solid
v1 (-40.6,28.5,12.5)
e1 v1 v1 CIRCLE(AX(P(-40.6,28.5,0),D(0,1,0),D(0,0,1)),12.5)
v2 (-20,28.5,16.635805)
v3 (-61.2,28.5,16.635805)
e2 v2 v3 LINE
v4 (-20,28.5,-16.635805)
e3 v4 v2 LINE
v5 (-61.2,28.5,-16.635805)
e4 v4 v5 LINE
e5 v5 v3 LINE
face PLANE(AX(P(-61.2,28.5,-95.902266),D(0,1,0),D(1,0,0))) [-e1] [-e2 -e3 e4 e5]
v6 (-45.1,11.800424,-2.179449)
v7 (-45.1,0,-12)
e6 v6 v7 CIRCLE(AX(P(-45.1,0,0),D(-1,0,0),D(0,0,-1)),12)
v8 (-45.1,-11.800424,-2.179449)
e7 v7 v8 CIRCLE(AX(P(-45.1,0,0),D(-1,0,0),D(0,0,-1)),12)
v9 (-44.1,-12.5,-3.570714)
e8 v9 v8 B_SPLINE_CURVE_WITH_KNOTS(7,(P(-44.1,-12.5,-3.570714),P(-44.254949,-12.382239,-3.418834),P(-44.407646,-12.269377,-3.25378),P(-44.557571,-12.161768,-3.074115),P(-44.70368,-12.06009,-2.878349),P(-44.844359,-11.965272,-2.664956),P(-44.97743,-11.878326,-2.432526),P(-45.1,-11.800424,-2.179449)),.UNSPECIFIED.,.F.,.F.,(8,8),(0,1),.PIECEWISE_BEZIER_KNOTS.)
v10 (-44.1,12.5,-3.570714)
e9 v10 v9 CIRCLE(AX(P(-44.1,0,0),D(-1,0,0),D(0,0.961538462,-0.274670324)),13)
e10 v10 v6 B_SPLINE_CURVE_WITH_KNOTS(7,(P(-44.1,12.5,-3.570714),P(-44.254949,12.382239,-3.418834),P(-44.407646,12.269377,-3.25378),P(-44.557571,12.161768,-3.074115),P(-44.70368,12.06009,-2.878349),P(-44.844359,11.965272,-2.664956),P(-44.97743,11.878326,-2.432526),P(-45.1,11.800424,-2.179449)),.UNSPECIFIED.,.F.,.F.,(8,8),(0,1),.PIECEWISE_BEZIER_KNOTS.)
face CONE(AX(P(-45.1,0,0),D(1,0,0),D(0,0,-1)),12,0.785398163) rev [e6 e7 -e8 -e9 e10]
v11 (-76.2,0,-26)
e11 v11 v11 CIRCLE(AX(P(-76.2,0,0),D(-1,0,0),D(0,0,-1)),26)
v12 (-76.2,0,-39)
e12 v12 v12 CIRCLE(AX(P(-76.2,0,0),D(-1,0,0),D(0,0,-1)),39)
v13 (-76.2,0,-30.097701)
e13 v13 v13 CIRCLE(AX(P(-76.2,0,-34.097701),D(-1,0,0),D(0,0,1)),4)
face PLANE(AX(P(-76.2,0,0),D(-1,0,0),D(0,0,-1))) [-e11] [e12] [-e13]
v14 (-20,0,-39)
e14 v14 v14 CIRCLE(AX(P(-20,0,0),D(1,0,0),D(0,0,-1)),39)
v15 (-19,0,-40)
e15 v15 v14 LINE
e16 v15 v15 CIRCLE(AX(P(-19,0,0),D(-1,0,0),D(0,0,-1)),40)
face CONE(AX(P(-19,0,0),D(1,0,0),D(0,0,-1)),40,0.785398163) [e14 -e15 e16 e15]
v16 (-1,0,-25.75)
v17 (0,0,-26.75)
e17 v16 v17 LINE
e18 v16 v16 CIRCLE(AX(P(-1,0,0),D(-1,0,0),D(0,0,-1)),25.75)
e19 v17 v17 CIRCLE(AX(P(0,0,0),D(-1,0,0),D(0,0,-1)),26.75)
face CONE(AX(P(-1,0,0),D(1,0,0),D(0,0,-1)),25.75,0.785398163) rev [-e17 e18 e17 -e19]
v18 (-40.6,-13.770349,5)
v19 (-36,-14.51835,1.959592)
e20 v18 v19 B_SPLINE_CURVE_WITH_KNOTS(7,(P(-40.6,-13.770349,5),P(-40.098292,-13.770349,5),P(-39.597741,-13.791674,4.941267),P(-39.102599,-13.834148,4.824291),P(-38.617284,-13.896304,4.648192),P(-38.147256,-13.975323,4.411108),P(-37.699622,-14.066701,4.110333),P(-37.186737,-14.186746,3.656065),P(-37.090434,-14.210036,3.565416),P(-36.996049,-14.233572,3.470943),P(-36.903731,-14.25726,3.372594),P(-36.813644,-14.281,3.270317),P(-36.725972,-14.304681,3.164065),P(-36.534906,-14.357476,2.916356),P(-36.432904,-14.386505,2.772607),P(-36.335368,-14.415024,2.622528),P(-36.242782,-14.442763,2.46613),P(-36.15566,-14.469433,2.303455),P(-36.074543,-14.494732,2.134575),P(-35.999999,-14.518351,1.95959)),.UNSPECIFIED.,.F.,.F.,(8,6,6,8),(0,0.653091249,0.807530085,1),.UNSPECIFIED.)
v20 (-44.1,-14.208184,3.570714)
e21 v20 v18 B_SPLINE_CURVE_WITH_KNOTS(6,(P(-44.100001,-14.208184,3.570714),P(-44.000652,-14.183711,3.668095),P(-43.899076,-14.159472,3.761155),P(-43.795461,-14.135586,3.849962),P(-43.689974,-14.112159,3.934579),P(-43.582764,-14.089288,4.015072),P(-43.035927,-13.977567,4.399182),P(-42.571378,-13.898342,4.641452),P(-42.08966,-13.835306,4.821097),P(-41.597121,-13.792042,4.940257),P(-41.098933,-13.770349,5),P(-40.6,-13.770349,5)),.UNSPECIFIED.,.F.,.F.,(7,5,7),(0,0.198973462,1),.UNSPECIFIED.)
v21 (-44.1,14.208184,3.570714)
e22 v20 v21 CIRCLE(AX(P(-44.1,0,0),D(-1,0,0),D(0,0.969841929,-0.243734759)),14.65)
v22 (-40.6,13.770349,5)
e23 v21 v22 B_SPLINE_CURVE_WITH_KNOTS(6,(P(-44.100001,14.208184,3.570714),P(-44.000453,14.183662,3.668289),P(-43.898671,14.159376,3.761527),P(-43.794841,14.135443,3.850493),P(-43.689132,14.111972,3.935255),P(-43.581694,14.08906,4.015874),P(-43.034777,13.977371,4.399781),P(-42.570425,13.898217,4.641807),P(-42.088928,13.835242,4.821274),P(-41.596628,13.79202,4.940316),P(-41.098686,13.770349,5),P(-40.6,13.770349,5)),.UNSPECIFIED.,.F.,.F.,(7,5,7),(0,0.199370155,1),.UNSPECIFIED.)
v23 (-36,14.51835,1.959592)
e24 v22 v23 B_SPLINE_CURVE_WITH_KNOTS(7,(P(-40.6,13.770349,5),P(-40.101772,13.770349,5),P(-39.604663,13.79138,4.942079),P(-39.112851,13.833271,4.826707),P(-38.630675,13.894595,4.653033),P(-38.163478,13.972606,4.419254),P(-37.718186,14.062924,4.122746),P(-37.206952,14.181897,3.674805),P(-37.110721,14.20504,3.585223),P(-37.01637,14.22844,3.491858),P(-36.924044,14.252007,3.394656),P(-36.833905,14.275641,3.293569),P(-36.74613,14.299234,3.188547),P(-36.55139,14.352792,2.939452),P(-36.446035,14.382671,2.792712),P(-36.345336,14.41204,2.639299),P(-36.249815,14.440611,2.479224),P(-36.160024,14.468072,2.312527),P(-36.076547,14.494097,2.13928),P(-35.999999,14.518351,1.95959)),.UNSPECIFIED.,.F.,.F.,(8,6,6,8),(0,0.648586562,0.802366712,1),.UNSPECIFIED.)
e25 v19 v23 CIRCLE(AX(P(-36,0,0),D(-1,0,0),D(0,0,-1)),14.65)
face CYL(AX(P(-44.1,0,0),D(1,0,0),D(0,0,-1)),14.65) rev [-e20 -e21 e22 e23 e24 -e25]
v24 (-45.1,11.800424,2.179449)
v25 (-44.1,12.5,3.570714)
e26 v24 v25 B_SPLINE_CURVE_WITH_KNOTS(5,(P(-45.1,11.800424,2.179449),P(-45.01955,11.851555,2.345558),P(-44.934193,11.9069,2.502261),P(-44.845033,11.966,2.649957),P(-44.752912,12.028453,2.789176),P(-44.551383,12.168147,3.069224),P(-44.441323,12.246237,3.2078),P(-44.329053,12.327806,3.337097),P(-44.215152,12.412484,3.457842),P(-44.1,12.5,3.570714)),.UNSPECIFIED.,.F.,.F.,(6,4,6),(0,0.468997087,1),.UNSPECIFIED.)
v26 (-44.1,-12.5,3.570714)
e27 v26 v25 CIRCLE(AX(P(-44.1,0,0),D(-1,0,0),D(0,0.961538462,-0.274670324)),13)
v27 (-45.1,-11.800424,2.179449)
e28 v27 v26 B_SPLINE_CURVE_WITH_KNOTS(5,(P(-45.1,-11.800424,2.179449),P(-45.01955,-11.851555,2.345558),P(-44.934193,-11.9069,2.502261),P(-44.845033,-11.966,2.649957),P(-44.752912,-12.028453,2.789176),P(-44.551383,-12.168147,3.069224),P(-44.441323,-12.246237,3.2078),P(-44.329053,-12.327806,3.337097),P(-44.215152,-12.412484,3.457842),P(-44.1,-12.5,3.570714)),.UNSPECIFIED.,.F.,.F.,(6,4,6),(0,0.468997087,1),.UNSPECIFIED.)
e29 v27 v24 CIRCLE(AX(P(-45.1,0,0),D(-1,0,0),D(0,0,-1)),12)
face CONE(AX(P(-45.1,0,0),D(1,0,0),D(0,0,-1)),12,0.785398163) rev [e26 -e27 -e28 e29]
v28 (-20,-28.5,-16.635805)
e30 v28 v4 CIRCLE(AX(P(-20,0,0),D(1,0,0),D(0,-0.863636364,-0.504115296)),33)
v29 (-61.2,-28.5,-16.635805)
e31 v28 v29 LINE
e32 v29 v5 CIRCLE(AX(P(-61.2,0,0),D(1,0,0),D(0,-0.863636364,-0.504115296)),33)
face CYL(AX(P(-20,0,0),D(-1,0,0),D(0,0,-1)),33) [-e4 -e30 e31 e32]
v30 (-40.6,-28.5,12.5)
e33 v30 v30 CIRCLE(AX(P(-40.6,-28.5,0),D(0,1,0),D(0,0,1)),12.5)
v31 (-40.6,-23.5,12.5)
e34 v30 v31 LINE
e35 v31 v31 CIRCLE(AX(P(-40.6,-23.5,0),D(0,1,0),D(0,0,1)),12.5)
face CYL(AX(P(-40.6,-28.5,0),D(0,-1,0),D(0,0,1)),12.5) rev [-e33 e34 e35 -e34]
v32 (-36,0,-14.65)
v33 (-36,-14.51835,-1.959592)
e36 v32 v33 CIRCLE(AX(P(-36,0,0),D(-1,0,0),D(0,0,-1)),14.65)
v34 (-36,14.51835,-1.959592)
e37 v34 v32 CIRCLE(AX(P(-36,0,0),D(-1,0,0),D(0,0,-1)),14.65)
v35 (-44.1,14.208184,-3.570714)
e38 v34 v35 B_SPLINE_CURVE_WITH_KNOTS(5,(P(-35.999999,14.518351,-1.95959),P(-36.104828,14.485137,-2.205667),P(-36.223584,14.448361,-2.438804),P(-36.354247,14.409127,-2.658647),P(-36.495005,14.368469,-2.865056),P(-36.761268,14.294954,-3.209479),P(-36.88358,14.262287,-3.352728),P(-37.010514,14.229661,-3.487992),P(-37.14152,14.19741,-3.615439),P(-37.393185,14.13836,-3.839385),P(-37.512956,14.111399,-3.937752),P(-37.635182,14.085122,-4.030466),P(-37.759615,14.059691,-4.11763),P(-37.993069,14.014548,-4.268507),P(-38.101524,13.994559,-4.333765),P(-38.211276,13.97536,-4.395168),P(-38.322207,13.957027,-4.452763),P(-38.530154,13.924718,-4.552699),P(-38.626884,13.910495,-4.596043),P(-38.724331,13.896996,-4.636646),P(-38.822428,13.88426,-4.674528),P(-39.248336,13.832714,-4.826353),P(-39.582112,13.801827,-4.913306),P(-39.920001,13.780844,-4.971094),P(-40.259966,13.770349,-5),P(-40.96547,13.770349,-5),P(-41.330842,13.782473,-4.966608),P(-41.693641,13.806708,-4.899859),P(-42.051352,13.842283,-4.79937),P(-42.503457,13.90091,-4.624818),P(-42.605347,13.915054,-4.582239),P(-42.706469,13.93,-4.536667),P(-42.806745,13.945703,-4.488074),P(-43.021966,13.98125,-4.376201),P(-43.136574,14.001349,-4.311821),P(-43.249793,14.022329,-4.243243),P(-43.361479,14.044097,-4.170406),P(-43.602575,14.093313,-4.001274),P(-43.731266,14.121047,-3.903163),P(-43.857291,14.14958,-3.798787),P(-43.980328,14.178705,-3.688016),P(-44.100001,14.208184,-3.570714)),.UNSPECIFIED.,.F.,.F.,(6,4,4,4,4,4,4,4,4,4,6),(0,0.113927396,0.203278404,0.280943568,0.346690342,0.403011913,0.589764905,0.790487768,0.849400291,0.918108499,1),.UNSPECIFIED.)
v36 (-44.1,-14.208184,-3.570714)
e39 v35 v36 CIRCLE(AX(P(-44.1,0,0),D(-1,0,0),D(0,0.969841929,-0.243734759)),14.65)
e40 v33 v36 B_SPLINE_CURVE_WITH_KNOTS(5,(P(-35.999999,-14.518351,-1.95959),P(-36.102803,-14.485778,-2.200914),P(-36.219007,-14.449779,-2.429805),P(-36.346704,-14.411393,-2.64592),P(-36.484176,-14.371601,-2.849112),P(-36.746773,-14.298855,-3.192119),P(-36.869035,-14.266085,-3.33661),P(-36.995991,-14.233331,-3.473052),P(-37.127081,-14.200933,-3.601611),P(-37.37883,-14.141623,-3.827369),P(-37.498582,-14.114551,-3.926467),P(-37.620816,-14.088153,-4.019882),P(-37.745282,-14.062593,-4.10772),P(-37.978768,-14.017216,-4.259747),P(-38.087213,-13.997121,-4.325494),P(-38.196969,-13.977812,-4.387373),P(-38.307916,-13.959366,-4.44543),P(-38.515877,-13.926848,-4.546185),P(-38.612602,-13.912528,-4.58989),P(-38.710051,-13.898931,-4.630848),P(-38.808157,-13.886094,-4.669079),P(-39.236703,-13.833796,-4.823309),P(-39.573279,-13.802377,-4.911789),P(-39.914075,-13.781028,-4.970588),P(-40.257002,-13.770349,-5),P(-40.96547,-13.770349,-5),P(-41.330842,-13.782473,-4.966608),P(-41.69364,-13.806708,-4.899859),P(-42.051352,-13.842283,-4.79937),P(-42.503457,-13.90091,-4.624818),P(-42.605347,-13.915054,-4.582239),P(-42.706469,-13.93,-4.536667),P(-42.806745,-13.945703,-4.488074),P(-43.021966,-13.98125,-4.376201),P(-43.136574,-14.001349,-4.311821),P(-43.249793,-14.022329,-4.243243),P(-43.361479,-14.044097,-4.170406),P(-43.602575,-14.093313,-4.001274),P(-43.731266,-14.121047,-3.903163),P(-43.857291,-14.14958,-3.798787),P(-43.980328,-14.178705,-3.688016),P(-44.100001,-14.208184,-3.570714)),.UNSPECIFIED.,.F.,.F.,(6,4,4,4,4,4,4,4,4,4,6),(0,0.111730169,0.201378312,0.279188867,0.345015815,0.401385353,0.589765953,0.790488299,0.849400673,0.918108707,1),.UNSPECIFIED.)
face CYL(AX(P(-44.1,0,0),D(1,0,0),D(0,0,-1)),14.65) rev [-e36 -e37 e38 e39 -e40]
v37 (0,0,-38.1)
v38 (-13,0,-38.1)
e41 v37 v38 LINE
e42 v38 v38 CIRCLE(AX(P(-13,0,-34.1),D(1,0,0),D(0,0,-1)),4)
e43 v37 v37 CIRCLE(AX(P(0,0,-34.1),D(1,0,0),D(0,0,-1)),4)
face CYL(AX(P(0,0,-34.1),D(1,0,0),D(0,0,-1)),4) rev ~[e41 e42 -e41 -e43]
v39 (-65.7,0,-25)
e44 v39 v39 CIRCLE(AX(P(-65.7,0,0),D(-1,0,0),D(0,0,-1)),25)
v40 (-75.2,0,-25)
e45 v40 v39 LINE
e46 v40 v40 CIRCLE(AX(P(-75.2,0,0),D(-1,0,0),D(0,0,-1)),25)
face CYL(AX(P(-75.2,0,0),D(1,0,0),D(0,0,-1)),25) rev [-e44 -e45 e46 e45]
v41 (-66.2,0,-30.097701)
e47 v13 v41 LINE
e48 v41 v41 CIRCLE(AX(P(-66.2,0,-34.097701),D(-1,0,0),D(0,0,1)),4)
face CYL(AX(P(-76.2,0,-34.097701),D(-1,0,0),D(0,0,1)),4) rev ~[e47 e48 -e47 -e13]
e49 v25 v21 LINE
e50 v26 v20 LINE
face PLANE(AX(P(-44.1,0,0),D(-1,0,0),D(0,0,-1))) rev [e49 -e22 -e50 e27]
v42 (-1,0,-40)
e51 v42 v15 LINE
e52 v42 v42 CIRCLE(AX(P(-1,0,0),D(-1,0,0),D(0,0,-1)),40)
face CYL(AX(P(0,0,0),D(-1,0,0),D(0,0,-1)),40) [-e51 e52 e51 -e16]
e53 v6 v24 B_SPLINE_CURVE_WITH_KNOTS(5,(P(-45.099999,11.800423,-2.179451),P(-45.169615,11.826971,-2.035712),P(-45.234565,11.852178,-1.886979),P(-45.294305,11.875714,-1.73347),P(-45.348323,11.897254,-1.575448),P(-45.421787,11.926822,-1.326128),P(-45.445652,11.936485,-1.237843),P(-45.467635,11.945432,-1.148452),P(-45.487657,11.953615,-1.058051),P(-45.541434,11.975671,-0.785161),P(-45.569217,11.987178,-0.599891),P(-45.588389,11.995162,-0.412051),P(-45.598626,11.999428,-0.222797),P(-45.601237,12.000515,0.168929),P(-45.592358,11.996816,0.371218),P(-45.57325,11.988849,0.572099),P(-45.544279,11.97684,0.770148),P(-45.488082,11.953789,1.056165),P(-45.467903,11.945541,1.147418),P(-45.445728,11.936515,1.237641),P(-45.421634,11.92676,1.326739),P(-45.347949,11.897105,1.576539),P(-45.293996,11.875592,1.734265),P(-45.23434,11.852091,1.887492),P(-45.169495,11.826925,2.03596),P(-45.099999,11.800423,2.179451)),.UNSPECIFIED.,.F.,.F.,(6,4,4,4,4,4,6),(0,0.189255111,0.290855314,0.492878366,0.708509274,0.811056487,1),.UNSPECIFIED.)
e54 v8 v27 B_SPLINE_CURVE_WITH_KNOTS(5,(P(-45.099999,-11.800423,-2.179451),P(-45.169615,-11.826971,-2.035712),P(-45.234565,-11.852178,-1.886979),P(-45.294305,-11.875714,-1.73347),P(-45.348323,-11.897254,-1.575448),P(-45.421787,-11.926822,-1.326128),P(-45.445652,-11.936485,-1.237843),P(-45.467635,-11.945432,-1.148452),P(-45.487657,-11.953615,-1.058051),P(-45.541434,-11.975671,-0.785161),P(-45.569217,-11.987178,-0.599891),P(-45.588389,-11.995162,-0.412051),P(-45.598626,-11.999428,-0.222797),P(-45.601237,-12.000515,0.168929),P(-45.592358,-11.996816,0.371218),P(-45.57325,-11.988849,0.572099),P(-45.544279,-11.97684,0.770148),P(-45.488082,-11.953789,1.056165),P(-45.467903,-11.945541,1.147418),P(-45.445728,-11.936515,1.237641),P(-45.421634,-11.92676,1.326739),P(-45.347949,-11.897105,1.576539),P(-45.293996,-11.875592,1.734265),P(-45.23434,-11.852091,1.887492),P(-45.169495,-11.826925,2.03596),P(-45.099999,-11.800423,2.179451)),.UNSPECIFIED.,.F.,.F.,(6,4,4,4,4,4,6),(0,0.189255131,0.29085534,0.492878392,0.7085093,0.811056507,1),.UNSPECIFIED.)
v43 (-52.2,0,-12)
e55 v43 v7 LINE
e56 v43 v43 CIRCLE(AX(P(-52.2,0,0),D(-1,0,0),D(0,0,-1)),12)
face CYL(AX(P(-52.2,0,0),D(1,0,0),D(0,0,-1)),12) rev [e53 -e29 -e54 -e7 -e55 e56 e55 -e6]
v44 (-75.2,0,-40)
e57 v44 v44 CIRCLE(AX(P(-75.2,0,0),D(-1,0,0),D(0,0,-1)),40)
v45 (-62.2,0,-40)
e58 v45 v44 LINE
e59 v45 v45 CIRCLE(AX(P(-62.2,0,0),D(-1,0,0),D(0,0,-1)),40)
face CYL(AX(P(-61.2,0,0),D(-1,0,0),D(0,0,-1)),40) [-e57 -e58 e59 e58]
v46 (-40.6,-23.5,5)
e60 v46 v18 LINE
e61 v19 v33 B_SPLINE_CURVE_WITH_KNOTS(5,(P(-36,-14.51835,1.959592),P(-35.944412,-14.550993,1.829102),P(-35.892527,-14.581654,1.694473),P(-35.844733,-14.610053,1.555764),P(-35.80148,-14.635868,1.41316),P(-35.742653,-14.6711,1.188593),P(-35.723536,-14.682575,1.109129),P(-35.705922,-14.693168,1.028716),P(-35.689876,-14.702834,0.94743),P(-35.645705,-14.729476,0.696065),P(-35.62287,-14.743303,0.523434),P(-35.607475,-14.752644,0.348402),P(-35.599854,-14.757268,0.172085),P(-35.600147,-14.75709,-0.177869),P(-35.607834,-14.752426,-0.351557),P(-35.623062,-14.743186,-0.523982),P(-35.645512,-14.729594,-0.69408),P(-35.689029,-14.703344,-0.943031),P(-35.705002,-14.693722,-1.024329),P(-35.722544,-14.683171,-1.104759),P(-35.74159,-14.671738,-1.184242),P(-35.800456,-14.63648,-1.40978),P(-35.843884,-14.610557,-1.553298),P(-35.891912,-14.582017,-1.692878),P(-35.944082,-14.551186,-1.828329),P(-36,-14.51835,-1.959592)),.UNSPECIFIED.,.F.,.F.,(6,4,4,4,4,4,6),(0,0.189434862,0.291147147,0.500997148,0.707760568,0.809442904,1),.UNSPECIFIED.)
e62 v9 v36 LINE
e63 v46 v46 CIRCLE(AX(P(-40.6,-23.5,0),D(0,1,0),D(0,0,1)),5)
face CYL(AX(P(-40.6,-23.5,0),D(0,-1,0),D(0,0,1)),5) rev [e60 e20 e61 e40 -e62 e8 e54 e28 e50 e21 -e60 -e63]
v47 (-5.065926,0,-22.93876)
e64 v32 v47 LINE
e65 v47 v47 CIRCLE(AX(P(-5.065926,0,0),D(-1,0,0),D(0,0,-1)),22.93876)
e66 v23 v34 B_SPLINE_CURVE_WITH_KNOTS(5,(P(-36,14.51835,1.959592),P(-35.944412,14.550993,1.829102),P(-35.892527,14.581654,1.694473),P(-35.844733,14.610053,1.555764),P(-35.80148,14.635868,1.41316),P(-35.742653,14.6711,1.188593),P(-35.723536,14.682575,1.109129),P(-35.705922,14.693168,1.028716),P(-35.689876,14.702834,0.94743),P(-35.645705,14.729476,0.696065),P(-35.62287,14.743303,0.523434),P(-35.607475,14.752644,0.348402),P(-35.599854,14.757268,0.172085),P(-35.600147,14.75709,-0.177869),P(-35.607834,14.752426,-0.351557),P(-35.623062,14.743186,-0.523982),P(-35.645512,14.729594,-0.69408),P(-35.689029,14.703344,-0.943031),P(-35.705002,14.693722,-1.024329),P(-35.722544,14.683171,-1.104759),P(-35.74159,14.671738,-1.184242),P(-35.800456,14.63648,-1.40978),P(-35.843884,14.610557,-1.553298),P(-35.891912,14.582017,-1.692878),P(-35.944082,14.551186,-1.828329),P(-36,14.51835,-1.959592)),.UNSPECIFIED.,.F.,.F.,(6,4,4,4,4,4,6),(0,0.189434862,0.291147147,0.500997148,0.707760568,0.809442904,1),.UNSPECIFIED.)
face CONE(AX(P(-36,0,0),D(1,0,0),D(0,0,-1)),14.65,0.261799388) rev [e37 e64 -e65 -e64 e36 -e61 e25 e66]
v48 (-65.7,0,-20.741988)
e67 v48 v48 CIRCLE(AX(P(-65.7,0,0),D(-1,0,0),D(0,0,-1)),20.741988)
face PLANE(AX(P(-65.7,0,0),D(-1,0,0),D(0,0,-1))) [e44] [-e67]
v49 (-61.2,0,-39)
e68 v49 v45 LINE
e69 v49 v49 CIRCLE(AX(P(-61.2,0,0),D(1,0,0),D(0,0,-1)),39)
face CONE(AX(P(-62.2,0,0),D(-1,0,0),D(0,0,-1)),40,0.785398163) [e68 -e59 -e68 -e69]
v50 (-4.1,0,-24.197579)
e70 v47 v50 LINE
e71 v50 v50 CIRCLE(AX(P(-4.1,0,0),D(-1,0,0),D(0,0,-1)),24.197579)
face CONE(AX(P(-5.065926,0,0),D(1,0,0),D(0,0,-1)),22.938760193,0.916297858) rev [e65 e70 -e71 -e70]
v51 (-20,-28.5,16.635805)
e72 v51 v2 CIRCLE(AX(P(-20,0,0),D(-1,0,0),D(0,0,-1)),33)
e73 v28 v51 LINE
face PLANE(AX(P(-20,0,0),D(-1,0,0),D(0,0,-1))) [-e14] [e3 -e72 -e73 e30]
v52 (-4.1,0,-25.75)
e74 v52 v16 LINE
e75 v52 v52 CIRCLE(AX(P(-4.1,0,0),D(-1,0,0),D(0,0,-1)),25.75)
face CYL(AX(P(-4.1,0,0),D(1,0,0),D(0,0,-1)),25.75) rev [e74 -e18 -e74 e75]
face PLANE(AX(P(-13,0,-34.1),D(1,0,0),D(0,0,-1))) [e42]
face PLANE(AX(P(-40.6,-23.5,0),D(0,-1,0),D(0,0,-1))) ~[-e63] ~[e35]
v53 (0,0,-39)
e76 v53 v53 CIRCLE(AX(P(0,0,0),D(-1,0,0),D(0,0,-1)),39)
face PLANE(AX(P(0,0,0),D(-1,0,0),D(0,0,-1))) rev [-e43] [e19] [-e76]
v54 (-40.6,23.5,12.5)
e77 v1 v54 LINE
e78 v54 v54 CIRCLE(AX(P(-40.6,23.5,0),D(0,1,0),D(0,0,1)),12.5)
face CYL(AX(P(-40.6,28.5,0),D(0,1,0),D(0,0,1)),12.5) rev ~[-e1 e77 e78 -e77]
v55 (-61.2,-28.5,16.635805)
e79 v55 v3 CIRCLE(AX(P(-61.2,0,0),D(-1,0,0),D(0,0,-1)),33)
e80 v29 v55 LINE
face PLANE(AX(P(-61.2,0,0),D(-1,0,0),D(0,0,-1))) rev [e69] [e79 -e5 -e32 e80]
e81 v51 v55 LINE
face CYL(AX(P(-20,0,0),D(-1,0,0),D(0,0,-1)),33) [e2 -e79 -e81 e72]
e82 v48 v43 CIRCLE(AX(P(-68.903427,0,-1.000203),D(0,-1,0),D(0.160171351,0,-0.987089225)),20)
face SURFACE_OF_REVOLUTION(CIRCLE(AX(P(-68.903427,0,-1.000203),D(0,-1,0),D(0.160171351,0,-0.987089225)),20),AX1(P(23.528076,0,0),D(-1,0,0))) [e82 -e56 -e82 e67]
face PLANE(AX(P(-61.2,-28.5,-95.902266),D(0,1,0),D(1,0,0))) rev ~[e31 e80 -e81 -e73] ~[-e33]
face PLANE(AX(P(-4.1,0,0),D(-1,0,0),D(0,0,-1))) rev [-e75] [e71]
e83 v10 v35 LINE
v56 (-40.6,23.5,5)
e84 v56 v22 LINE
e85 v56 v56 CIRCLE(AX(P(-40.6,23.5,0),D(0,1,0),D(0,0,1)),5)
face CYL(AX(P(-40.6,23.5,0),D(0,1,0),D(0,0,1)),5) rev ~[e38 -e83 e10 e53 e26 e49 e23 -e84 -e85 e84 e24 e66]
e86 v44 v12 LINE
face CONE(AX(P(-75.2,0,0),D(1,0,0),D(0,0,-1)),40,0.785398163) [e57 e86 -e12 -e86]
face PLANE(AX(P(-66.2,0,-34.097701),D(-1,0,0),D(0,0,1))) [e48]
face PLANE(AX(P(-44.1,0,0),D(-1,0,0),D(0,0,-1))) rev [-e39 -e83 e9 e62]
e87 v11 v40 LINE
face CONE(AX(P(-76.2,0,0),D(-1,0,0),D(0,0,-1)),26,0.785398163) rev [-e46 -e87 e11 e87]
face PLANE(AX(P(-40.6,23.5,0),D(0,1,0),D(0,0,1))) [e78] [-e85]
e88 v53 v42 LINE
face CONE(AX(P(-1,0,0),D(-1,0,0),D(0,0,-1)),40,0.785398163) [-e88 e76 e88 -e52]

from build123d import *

# Parameters (mm, degrees)
CHAMFER1_SIZE           = 1
CUT_EXTRUDE1_DEPTH      = 95.902265516
CUT_EXTRUDE1_DEPTH_BACK = 95.902265516
SKETCH2_W               = 41.2
SKETCH2_H               = 27.770788335
SKETCH2_H_2             = 30.82392473
SKETCH3_R               = 12.5
CUT_EXTRUDE2_DEPTH      = 5
SKETCH4_R               = 5
CUT_EXTRUDE3_DEPTH      = 19
SKETCH5_R               = 4
CUT_EXTRUDE4_DEPTH      = 10
SKETCH6_R               = 4
CUT_EXTRUDE5_DEPTH      = 13


with BuildPart() as part:
    # Sketch1 → Revolve1 (revolve)
    with BuildSketch(Plane.XY, mode=Mode.PRIVATE) as revolve1_sk:
        with BuildLine():
            Line((0, 26.75), (0, 40))
            Line((0, 40), (-20, 40))
            Line((-20, 40), (-20, 33))
            Line((-20, 33), (-61.2, 33))
            Line((-61.2, 33), (-61.2, 40))
            Line((-61.2, 40), (-76.2, 40))
            Line((-76.2, 40), (-76.2, 26))
            Line((-76.2, 26), (-75.2, 25))
            Line((-75.2, 25), (-65.7, 25))
            Line((-65.7, 25), (-65.7, 20.741987874))
            ThreePointArc((-65.7, 20.741987874), (-58.03253481, 17.787808996), (-52.2, 12))
            Line((-52.2, 12), (-45.1, 12))
            Line((-45.1, 12), (-44.1, 13))
            Line((-44.1, 13), (-44.1, 14.65))
            Line((-44.1, 14.65), (-36, 14.65))
            Line((-36, 14.65), (-5.065925826, 22.938760193))
            Line((-5.065925826, 22.938760193), (-4.1, 24.197579239))
            Line((-4.1, 24.197579239), (-4.1, 25.75))
            Line((-4.1, 25.75), (-1, 25.75))
            Line((-1, 25.75), (0, 26.75))
        make_face()
    revolve(revolve1_sk.sketch.rotate(Axis((23.528076115, 0, 0), (-1, 0, 0)), 90), axis=Axis((23.528076115, 0, 0), (-1, 0, 0)))

    # Chamfer1
    chamfer1_edges = [part.edges().sort_by_distance(p)[0] for p in [
        (0, 0, 40),
        (-20, 0, 40),
        (-61.2, 0, 40),
        (-76.2, 0, 40),
    ]]
    chamfer(chamfer1_edges, length=CHAMFER1_SIZE)

    # Sketch2 → Cut-Extrude1 (cut, two sides: drawn at the far end of the back side and taken through both)
    with BuildSketch(Plane.XY.offset(-CUT_EXTRUDE1_DEPTH_BACK)):
        with Locations((-40.6, 42.385394168)):
            Rectangle(SKETCH2_W, SKETCH2_H)
        with Locations((-40.6, -43.911962365)):
            Rectangle(SKETCH2_W, SKETCH2_H_2)
    extrude(amount=CUT_EXTRUDE1_DEPTH + CUT_EXTRUDE1_DEPTH_BACK, mode=Mode.SUBTRACT)

    # Sketch3 → Cut-Extrude2 (cut)
    with BuildSketch(Plane(origin=(0, 28.5, 0), x_dir=(1, 0, 0), z_dir=(0, 1, 0))):
        with Locations(Location((-40.6, 0, 0), (0, 0, 270))):
            Circle(SKETCH3_R)
    cut_extrude2 = extrude(amount=-CUT_EXTRUDE2_DEPTH, mode=Mode.SUBTRACT)

    # Sketch4 → Cut-Extrude3 (cut)
    with BuildSketch(Plane(origin=(0, 23.5, 0), x_dir=(1, 0, 0), z_dir=(0, 1, 0))):
        with Locations(Location((-40.6, 0, 0), (0, 0, 270))):
            Circle(SKETCH4_R)
    cut_extrude3 = extrude(amount=-CUT_EXTRUDE3_DEPTH, mode=Mode.SUBTRACT)

    # Mirror1: Cut-Extrude2, Cut-Extrude3 across plane
    add(cut_extrude2.mirror(Plane.ZX), mode=Mode.SUBTRACT)
    add(cut_extrude3.mirror(Plane.ZX), mode=Mode.SUBTRACT)

    # Sketch5 → Cut-Extrude4 (cut)
    with BuildSketch(Plane.ZY.offset(76.2)):
        with Locations((-34.097701423, 0)):
            Circle(SKETCH5_R)
    extrude(amount=-CUT_EXTRUDE4_DEPTH, mode=Mode.SUBTRACT)

    # Sketch6 → Cut-Extrude5 (cut)
    with BuildSketch(Plane(origin=(0, 0, 0), x_dir=(0, 0, -1), z_dir=(1, 0, 0))):
        with Locations((34.1, 0)):
            Circle(SKETCH6_R)
    extrude(amount=-CUT_EXTRUDE5_DEPTH, mode=Mode.SUBTRACT)


solid = part.part
